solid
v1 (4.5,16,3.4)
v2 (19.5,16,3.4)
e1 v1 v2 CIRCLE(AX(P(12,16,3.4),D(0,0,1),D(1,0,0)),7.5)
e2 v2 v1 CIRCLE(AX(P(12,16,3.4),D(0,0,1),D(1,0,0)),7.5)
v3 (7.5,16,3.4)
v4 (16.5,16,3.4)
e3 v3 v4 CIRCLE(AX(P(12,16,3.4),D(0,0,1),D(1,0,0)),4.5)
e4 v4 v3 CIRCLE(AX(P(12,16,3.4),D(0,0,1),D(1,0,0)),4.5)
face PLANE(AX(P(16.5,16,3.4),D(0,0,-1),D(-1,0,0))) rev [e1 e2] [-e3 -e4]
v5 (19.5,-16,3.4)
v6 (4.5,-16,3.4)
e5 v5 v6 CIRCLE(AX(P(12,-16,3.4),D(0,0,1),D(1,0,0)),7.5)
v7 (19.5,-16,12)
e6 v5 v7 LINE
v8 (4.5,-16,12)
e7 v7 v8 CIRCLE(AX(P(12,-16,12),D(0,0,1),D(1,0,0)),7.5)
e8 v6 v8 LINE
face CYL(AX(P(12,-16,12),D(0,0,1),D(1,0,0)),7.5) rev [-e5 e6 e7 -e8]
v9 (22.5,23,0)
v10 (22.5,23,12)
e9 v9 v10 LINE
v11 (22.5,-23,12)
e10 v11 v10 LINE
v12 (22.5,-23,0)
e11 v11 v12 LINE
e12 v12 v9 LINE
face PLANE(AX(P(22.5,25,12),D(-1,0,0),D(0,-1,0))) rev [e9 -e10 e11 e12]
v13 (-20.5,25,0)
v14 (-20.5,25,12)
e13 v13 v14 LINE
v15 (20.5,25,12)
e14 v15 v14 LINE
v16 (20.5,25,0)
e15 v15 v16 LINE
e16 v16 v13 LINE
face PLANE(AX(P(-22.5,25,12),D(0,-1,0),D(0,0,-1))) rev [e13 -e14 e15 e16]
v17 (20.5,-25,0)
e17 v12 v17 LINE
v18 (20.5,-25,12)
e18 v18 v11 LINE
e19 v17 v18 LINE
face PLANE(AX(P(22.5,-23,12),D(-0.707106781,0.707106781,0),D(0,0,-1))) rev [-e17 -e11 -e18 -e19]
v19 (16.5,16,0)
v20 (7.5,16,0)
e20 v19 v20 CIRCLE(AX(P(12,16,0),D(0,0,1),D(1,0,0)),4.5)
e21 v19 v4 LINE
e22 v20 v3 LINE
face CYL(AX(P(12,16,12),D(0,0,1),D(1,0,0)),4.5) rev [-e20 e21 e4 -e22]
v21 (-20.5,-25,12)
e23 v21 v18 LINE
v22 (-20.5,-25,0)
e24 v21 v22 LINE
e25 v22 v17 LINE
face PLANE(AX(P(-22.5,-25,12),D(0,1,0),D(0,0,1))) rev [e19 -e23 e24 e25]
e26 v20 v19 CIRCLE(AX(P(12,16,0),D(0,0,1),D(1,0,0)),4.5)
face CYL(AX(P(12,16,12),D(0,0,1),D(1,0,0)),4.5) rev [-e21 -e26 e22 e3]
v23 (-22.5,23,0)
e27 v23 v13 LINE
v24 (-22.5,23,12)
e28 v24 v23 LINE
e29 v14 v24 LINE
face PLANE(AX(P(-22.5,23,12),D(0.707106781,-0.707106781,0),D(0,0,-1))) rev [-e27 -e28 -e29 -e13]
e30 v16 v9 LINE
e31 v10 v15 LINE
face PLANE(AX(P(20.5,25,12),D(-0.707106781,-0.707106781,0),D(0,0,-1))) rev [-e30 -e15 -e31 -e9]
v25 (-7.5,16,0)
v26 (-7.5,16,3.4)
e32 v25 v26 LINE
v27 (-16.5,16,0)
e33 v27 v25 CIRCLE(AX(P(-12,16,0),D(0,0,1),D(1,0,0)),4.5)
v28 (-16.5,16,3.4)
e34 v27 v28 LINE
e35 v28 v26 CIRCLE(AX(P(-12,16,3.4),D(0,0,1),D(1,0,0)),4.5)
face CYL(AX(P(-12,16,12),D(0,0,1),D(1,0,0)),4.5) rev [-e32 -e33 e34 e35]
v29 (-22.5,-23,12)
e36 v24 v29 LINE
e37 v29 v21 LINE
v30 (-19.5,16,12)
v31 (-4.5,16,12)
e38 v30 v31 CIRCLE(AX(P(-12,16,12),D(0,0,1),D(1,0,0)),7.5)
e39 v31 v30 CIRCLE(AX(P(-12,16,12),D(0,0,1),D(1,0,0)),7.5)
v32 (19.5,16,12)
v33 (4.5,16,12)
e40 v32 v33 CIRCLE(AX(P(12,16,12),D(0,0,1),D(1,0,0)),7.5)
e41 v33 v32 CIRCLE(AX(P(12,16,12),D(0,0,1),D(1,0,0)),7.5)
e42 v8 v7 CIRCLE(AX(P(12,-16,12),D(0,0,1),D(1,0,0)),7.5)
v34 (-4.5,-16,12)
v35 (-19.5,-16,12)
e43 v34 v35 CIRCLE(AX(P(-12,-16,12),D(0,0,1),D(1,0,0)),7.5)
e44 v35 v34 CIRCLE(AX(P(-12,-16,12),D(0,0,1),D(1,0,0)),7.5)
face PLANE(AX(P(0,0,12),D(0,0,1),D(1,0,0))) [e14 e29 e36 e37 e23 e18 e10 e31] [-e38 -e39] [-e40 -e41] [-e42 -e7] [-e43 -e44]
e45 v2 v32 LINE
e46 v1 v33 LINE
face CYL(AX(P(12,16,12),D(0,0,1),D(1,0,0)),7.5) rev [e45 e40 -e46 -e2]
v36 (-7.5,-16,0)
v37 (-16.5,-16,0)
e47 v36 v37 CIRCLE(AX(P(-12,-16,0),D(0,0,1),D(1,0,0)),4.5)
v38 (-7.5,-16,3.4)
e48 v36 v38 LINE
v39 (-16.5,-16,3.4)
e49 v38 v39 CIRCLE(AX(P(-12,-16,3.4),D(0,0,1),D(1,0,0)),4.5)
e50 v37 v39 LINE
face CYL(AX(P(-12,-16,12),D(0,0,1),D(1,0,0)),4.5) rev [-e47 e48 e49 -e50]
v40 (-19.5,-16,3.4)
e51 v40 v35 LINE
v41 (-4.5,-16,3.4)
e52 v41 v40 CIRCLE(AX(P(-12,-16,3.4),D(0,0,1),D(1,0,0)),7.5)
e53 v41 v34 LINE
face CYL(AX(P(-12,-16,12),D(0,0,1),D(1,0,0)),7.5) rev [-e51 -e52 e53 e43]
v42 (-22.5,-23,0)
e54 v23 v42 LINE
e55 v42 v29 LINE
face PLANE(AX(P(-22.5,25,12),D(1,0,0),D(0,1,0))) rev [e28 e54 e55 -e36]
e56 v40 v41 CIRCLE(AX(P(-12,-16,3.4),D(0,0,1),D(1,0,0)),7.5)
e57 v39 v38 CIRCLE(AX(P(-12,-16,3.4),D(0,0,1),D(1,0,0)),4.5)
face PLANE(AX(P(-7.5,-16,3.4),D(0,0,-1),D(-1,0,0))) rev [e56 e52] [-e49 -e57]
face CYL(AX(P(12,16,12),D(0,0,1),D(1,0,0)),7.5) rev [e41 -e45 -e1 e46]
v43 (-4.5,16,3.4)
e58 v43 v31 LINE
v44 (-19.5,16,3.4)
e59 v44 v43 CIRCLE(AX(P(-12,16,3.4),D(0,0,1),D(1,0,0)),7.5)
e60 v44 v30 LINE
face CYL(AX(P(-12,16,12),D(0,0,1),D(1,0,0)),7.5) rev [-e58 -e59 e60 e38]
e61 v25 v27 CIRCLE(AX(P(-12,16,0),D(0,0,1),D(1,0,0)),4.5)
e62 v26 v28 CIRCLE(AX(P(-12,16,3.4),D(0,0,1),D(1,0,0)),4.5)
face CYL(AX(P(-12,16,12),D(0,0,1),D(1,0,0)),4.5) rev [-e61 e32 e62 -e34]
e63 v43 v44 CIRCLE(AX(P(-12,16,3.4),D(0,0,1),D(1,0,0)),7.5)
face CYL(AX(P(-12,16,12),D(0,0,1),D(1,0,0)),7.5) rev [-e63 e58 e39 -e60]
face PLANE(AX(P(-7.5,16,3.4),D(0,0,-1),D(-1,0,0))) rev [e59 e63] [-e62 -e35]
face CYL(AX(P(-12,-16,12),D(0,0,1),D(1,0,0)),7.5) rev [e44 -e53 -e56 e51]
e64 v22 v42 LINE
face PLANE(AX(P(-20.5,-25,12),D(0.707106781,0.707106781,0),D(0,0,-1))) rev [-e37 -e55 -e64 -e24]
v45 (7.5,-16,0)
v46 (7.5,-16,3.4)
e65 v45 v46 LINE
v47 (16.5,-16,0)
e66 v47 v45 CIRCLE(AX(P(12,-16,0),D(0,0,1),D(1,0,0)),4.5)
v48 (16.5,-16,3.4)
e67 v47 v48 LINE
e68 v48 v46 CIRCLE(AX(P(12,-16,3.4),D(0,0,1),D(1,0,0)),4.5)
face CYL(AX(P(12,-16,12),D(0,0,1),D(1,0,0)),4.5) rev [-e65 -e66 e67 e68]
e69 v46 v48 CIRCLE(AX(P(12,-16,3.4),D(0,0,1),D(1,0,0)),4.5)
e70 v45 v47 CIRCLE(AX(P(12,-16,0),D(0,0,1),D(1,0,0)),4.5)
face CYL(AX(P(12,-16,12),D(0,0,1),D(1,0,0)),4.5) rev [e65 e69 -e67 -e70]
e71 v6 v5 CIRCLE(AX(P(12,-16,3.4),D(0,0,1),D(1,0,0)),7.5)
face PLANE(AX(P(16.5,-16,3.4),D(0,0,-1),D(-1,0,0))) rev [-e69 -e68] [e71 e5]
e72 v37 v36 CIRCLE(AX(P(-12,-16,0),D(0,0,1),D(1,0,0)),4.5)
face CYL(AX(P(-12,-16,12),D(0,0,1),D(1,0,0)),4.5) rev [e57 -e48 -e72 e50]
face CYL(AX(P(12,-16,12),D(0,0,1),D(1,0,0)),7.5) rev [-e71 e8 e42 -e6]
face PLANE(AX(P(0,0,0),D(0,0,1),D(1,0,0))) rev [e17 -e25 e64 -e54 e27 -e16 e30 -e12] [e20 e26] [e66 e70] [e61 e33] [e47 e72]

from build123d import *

# Parameters (mm, degrees)
SKETCH1_W                                           = 45
SKETCH1_H                                           = 50
BOSS_EXTRUDE1_DEPTH                                 = 12
CBORE_FOR_M8_HEX_SOCKET_HEAD_CAP_SCREW1_D           = 9
CBORE_FOR_M8_HEX_SOCKET_HEAD_CAP_SCREW1_CBORE_D     = 15
CBORE_FOR_M8_HEX_SOCKET_HEAD_CAP_SCREW1_CBORE_DEPTH = 8.6
CHAMFER1_SIZE                                       = 2


with BuildPart() as part:
    # Sketch1 → Boss-Extrude1 (new body)
    with BuildSketch(Plane.XY):
        Rectangle(SKETCH1_W, SKETCH1_H)
    extrude(amount=BOSS_EXTRUDE1_DEPTH)

    # CBORE for M8 Hex Socket Head Cap Screw1 (through all)
    with Locations(Plane.XY.offset(12)):
        with Locations((-12, 16), (12, 16), (12, -16), (-12, -16)):
            CounterBoreHole(CBORE_FOR_M8_HEX_SOCKET_HEAD_CAP_SCREW1_D / 2, CBORE_FOR_M8_HEX_SOCKET_HEAD_CAP_SCREW1_CBORE_D / 2, CBORE_FOR_M8_HEX_SOCKET_HEAD_CAP_SCREW1_CBORE_DEPTH)

    # Chamfer1
    chamfer1_edges = [part.edges().sort_by_distance(p)[0] for p in [
        (22.5, -25, 6),
        (-22.5, -25, 6),
        (-22.5, 25, 6),
        (22.5, 25, 6),
    ]]
    chamfer(chamfer1_edges, length=CHAMFER1_SIZE)


solid = part.part
